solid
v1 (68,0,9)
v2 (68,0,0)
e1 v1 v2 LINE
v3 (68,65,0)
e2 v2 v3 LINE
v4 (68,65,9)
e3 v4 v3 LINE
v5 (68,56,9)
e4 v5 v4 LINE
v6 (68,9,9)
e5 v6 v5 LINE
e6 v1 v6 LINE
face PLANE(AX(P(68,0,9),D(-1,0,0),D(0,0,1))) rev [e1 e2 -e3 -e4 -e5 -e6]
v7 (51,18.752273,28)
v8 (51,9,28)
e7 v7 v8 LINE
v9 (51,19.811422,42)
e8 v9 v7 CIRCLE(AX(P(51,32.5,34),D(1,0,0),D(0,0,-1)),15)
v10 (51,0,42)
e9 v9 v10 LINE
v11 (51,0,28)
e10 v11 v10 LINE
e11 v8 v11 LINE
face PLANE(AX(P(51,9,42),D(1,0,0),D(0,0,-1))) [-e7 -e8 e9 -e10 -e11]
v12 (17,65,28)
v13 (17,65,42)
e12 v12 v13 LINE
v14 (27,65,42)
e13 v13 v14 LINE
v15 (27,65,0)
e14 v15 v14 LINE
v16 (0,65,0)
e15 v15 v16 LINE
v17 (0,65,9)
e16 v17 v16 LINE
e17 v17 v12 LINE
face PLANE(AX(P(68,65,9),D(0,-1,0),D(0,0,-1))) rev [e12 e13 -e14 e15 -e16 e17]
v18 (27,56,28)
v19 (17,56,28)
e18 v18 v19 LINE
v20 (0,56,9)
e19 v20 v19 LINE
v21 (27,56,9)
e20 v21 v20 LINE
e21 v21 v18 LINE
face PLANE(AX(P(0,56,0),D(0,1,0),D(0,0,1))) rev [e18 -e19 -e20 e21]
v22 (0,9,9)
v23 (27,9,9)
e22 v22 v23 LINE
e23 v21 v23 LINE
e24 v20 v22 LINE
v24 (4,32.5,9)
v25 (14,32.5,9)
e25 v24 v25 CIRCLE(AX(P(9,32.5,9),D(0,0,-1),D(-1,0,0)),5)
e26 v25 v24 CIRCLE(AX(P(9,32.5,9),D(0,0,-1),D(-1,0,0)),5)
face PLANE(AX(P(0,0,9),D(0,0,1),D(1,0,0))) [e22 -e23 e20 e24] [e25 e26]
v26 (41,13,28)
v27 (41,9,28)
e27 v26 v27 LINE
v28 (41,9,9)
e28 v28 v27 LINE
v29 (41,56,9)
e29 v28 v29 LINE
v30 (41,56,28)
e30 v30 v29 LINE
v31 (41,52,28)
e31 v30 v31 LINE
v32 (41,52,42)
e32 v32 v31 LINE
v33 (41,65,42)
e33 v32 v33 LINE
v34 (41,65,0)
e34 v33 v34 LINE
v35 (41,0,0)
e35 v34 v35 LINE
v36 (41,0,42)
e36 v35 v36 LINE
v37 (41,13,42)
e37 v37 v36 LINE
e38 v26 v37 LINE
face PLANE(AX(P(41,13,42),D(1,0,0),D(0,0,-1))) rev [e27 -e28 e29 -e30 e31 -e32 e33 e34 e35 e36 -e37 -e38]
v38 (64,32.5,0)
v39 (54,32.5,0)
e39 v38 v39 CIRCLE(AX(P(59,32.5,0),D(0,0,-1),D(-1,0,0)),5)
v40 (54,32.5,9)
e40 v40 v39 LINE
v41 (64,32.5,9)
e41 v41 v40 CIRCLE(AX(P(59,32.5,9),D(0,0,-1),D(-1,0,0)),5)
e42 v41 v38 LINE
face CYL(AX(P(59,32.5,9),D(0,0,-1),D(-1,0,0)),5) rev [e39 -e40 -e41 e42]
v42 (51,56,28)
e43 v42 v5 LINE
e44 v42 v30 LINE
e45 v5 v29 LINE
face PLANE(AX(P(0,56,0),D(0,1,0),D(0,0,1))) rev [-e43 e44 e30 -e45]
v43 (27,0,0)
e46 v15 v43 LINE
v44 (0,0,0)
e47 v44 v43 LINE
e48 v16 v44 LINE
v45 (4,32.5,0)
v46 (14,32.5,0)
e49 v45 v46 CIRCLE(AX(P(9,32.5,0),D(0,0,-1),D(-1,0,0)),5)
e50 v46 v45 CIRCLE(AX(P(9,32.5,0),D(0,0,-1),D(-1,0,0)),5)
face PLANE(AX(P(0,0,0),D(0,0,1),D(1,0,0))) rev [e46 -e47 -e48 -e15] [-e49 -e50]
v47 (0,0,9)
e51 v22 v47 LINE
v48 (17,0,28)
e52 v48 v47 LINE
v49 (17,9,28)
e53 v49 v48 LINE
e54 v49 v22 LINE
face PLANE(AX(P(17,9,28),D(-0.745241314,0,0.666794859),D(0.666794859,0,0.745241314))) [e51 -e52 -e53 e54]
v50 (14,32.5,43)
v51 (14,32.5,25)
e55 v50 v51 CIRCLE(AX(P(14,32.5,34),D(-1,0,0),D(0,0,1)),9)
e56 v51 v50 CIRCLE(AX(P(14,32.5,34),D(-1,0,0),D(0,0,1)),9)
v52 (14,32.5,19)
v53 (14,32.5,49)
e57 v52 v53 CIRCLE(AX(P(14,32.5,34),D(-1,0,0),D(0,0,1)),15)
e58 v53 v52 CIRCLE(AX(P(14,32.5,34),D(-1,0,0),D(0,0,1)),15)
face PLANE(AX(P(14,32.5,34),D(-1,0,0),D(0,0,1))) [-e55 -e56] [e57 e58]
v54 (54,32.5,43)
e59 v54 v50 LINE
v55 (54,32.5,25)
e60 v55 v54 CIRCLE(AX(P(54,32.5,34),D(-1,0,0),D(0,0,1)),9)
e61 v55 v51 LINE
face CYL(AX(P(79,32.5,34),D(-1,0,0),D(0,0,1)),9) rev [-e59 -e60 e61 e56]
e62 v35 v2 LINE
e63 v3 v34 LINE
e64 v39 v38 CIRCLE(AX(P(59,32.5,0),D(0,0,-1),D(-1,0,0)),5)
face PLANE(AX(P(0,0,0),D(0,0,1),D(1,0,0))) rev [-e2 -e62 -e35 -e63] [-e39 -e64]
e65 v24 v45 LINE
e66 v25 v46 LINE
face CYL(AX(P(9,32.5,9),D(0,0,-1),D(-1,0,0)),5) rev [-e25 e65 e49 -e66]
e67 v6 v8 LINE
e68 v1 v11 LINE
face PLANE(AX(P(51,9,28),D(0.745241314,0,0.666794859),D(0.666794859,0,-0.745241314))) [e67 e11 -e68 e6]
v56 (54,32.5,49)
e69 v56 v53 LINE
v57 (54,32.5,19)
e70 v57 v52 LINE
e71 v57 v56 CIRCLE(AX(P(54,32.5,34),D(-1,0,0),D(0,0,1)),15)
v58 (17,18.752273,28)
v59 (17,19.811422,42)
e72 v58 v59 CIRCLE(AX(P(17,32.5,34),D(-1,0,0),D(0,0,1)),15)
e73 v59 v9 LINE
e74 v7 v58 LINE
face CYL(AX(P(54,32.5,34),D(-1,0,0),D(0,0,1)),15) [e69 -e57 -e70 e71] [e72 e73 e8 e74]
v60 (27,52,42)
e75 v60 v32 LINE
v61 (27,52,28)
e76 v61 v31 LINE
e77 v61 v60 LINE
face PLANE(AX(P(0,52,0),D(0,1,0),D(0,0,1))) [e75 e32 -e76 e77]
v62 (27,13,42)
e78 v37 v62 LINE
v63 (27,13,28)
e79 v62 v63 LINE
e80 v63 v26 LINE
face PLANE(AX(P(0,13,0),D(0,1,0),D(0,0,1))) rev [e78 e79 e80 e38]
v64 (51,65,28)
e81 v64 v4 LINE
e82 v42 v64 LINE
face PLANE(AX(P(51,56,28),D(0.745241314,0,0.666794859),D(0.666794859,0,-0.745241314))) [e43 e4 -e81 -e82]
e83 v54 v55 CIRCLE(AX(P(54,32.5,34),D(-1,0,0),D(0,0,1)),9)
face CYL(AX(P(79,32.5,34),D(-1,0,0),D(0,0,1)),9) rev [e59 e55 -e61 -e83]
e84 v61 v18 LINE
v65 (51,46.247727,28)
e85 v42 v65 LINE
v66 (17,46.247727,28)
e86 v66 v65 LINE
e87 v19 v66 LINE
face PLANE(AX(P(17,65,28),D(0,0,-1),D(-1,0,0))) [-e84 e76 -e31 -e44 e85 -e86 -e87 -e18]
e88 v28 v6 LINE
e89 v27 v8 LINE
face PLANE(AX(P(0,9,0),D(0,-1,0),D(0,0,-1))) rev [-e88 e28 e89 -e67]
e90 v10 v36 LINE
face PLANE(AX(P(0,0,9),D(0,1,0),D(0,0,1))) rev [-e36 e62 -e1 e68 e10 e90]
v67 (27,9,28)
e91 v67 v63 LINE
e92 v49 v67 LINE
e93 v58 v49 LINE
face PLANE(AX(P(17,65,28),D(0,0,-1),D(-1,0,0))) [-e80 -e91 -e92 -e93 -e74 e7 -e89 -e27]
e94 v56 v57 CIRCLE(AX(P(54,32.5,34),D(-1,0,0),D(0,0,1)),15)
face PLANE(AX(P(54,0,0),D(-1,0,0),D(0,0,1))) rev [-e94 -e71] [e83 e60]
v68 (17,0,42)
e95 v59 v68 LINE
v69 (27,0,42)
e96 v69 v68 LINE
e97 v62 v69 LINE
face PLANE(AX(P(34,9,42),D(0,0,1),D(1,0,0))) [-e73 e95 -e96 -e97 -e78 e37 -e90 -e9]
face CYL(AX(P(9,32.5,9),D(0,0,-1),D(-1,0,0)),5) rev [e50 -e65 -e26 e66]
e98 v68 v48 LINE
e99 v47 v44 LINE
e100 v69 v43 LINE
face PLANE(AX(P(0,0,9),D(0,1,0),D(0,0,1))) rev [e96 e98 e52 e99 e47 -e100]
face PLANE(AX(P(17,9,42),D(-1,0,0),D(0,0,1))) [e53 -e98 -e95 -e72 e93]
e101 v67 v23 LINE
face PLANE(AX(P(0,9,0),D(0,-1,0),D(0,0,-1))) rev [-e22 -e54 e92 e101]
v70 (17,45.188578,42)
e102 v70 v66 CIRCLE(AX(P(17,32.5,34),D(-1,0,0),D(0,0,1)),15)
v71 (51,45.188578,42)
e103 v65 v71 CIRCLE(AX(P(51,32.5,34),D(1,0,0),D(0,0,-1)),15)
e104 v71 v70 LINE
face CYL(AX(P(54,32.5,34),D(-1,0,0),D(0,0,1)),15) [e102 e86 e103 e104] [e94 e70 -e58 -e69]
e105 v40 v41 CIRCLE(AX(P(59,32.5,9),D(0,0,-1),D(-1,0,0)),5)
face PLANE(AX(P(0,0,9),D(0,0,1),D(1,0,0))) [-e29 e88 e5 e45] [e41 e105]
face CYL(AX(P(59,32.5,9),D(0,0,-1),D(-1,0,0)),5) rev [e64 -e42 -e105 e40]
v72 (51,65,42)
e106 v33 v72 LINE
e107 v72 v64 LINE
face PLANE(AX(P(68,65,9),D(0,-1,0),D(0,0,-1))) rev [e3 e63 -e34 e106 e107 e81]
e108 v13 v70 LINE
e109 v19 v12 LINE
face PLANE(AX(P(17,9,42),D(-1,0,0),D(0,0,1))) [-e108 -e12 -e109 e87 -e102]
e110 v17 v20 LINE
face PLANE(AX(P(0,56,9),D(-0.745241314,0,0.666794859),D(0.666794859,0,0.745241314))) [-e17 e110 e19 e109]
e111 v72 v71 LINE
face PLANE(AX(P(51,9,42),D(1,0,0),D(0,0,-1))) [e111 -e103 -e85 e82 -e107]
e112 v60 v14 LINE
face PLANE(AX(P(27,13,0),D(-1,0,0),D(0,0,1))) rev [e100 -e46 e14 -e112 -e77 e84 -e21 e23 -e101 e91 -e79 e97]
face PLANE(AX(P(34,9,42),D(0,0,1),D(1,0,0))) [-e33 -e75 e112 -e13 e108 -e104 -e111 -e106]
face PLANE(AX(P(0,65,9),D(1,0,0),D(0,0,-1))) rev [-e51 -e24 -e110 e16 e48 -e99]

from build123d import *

# Parameters (mm, degrees)
BASE_PLATE_SKETCH_W        = 68
BASE_PLATE_SKETCH_H        = 65
BASE_PLATE_68X65_DEPTH     = 9
UPRIGHT_BLOCK_DEPTH        = 9
SECOND_UPRIGHT_BLOCK_DEPTH = 9
SIDE_WEB_SKETCH_W          = 34
SIDE_WEB_SKETCH_H          = 14
SIDE_WEB_DEPTH             = 65
UPPER_SLOT_7X14_DEPTH      = 13
LOWER_SLOT_7X14_DEPTH      = 13
THROUGH_CHANNEL_SKETCH_W   = 14
THROUGH_CHANNEL_SKETCH_H   = 9
THROUGH_CHANNEL_DEPTH      = 65
BEARING_HUB_SKETCH_R       = 15
BEARING_HUB_DEPTH          = 37
HUB_START                  = 3
HUB_COLLAR_SKETCH_30_R     = 15
HUB_COLLAR_30_DEPTH        = 3
CENTER_BORE_SKETCH_18_R    = 9
CENTER_BORE_18_DEPTH       = 65
SIDE_POCKET_SKETCH_R       = 5
SIDE_POCKET_CUT_DEPTH      = 9


with BuildPart() as part:
    # Base Plate Sketch → Base Plate 68x65 (new body)
    with BuildSketch(Plane.XY):
        with Locations((34, 32.5)):
            Rectangle(BASE_PLATE_SKETCH_W, BASE_PLATE_SKETCH_H)
    extrude(amount=BASE_PLATE_68X65_DEPTH)

    # Upright Block Sketch → Upright Block (add)
    with BuildSketch(Plane.XZ):
        Polygon((0, 9), (68, 9), (51, 28), (51, 42), (34, 42), (17, 42), (17, 28), align=None)
    extrude(amount=-UPRIGHT_BLOCK_DEPTH)

    # Second Upright Sketch → Second Upright Block (add)
    with BuildSketch(Plane(origin=(0, 65, 0), x_dir=(1, 0, 0), z_dir=(0, 1, 0))):
        Polygon((34, -42), (51, -42), (51, -28), (68, -9), (0, -9), (17, -28), (17, -42), align=None)
    extrude(amount=-SECOND_UPRIGHT_BLOCK_DEPTH)

    # Side Web Sketch → Side Web (add)
    with BuildSketch(Plane.XZ):
        with Locations((34, 35)):
            Rectangle(SIDE_WEB_SKETCH_W, SIDE_WEB_SKETCH_H)
    extrude(amount=-SIDE_WEB_DEPTH)

    # Upper Slot Sketch → Upper Slot 7x14 (cut)
    with BuildSketch(Plane.XZ):
        Polygon((34, 42), (41, 42), (41, 0), (27, 0), (27, 42), align=None)
    extrude(amount=-UPPER_SLOT_7X14_DEPTH, mode=Mode.SUBTRACT)

    # Lower Slot Sketch → Lower Slot 7x14 (cut)
    with BuildSketch(Plane(origin=(0, 65, 0), x_dir=(1, 0, 0), z_dir=(0, 1, 0))):
        Polygon((34, -42), (41, -42), (41, 0), (27, 0), (27, -42), align=None)
    extrude(amount=-LOWER_SLOT_7X14_DEPTH, mode=Mode.SUBTRACT)

    # Through Channel Sketch → Through Channel (cut)
    with BuildSketch(Plane.XZ.offset(-13)):
        with Locations((34, 4.5)):
            Rectangle(THROUGH_CHANNEL_SKETCH_W, THROUGH_CHANNEL_SKETCH_H)
    extrude(amount=-THROUGH_CHANNEL_DEPTH, mode=Mode.SUBTRACT)

    # Bearing Hub Sketch → Bearing Hub (add)
    with BuildSketch(Plane.ZY.offset(-17)):
        with Locations((34, 32.5)):
            Circle(BEARING_HUB_SKETCH_R)
    extrude(amount=-BEARING_HUB_DEPTH)

    # Hub Collar Sketch Ø30 → Hub Collar Ø30 (add)
    with BuildSketch(Plane.ZY.offset(-17).offset(HUB_START)):
        with Locations((34, 32.5)):
            Circle(HUB_COLLAR_SKETCH_30_R)
    extrude(amount=-HUB_COLLAR_30_DEPTH)

    # Center Bore Sketch Ø18 → Center Bore Ø18 (cut)
    with BuildSketch(Plane.ZY.offset(-14)):
        with Locations((34, 32.5)):
            Circle(CENTER_BORE_SKETCH_18_R)
    extrude(amount=-CENTER_BORE_18_DEPTH, mode=Mode.SUBTRACT)

    # Side Pocket Sketch → Side Pocket Cut (cut)
    with BuildSketch(Plane(origin=(0, 0, 0), x_dir=(-1, 0, 0), z_dir=(0, 0, -1))):
        with Locations((-59, 32.5)):
            Circle(SIDE_POCKET_SKETCH_R)
        with Locations((-9, 32.5)):
            Circle(SIDE_POCKET_SKETCH_R)
    extrude(amount=-SIDE_POCKET_CUT_DEPTH, mode=Mode.SUBTRACT)


solid = part.part
